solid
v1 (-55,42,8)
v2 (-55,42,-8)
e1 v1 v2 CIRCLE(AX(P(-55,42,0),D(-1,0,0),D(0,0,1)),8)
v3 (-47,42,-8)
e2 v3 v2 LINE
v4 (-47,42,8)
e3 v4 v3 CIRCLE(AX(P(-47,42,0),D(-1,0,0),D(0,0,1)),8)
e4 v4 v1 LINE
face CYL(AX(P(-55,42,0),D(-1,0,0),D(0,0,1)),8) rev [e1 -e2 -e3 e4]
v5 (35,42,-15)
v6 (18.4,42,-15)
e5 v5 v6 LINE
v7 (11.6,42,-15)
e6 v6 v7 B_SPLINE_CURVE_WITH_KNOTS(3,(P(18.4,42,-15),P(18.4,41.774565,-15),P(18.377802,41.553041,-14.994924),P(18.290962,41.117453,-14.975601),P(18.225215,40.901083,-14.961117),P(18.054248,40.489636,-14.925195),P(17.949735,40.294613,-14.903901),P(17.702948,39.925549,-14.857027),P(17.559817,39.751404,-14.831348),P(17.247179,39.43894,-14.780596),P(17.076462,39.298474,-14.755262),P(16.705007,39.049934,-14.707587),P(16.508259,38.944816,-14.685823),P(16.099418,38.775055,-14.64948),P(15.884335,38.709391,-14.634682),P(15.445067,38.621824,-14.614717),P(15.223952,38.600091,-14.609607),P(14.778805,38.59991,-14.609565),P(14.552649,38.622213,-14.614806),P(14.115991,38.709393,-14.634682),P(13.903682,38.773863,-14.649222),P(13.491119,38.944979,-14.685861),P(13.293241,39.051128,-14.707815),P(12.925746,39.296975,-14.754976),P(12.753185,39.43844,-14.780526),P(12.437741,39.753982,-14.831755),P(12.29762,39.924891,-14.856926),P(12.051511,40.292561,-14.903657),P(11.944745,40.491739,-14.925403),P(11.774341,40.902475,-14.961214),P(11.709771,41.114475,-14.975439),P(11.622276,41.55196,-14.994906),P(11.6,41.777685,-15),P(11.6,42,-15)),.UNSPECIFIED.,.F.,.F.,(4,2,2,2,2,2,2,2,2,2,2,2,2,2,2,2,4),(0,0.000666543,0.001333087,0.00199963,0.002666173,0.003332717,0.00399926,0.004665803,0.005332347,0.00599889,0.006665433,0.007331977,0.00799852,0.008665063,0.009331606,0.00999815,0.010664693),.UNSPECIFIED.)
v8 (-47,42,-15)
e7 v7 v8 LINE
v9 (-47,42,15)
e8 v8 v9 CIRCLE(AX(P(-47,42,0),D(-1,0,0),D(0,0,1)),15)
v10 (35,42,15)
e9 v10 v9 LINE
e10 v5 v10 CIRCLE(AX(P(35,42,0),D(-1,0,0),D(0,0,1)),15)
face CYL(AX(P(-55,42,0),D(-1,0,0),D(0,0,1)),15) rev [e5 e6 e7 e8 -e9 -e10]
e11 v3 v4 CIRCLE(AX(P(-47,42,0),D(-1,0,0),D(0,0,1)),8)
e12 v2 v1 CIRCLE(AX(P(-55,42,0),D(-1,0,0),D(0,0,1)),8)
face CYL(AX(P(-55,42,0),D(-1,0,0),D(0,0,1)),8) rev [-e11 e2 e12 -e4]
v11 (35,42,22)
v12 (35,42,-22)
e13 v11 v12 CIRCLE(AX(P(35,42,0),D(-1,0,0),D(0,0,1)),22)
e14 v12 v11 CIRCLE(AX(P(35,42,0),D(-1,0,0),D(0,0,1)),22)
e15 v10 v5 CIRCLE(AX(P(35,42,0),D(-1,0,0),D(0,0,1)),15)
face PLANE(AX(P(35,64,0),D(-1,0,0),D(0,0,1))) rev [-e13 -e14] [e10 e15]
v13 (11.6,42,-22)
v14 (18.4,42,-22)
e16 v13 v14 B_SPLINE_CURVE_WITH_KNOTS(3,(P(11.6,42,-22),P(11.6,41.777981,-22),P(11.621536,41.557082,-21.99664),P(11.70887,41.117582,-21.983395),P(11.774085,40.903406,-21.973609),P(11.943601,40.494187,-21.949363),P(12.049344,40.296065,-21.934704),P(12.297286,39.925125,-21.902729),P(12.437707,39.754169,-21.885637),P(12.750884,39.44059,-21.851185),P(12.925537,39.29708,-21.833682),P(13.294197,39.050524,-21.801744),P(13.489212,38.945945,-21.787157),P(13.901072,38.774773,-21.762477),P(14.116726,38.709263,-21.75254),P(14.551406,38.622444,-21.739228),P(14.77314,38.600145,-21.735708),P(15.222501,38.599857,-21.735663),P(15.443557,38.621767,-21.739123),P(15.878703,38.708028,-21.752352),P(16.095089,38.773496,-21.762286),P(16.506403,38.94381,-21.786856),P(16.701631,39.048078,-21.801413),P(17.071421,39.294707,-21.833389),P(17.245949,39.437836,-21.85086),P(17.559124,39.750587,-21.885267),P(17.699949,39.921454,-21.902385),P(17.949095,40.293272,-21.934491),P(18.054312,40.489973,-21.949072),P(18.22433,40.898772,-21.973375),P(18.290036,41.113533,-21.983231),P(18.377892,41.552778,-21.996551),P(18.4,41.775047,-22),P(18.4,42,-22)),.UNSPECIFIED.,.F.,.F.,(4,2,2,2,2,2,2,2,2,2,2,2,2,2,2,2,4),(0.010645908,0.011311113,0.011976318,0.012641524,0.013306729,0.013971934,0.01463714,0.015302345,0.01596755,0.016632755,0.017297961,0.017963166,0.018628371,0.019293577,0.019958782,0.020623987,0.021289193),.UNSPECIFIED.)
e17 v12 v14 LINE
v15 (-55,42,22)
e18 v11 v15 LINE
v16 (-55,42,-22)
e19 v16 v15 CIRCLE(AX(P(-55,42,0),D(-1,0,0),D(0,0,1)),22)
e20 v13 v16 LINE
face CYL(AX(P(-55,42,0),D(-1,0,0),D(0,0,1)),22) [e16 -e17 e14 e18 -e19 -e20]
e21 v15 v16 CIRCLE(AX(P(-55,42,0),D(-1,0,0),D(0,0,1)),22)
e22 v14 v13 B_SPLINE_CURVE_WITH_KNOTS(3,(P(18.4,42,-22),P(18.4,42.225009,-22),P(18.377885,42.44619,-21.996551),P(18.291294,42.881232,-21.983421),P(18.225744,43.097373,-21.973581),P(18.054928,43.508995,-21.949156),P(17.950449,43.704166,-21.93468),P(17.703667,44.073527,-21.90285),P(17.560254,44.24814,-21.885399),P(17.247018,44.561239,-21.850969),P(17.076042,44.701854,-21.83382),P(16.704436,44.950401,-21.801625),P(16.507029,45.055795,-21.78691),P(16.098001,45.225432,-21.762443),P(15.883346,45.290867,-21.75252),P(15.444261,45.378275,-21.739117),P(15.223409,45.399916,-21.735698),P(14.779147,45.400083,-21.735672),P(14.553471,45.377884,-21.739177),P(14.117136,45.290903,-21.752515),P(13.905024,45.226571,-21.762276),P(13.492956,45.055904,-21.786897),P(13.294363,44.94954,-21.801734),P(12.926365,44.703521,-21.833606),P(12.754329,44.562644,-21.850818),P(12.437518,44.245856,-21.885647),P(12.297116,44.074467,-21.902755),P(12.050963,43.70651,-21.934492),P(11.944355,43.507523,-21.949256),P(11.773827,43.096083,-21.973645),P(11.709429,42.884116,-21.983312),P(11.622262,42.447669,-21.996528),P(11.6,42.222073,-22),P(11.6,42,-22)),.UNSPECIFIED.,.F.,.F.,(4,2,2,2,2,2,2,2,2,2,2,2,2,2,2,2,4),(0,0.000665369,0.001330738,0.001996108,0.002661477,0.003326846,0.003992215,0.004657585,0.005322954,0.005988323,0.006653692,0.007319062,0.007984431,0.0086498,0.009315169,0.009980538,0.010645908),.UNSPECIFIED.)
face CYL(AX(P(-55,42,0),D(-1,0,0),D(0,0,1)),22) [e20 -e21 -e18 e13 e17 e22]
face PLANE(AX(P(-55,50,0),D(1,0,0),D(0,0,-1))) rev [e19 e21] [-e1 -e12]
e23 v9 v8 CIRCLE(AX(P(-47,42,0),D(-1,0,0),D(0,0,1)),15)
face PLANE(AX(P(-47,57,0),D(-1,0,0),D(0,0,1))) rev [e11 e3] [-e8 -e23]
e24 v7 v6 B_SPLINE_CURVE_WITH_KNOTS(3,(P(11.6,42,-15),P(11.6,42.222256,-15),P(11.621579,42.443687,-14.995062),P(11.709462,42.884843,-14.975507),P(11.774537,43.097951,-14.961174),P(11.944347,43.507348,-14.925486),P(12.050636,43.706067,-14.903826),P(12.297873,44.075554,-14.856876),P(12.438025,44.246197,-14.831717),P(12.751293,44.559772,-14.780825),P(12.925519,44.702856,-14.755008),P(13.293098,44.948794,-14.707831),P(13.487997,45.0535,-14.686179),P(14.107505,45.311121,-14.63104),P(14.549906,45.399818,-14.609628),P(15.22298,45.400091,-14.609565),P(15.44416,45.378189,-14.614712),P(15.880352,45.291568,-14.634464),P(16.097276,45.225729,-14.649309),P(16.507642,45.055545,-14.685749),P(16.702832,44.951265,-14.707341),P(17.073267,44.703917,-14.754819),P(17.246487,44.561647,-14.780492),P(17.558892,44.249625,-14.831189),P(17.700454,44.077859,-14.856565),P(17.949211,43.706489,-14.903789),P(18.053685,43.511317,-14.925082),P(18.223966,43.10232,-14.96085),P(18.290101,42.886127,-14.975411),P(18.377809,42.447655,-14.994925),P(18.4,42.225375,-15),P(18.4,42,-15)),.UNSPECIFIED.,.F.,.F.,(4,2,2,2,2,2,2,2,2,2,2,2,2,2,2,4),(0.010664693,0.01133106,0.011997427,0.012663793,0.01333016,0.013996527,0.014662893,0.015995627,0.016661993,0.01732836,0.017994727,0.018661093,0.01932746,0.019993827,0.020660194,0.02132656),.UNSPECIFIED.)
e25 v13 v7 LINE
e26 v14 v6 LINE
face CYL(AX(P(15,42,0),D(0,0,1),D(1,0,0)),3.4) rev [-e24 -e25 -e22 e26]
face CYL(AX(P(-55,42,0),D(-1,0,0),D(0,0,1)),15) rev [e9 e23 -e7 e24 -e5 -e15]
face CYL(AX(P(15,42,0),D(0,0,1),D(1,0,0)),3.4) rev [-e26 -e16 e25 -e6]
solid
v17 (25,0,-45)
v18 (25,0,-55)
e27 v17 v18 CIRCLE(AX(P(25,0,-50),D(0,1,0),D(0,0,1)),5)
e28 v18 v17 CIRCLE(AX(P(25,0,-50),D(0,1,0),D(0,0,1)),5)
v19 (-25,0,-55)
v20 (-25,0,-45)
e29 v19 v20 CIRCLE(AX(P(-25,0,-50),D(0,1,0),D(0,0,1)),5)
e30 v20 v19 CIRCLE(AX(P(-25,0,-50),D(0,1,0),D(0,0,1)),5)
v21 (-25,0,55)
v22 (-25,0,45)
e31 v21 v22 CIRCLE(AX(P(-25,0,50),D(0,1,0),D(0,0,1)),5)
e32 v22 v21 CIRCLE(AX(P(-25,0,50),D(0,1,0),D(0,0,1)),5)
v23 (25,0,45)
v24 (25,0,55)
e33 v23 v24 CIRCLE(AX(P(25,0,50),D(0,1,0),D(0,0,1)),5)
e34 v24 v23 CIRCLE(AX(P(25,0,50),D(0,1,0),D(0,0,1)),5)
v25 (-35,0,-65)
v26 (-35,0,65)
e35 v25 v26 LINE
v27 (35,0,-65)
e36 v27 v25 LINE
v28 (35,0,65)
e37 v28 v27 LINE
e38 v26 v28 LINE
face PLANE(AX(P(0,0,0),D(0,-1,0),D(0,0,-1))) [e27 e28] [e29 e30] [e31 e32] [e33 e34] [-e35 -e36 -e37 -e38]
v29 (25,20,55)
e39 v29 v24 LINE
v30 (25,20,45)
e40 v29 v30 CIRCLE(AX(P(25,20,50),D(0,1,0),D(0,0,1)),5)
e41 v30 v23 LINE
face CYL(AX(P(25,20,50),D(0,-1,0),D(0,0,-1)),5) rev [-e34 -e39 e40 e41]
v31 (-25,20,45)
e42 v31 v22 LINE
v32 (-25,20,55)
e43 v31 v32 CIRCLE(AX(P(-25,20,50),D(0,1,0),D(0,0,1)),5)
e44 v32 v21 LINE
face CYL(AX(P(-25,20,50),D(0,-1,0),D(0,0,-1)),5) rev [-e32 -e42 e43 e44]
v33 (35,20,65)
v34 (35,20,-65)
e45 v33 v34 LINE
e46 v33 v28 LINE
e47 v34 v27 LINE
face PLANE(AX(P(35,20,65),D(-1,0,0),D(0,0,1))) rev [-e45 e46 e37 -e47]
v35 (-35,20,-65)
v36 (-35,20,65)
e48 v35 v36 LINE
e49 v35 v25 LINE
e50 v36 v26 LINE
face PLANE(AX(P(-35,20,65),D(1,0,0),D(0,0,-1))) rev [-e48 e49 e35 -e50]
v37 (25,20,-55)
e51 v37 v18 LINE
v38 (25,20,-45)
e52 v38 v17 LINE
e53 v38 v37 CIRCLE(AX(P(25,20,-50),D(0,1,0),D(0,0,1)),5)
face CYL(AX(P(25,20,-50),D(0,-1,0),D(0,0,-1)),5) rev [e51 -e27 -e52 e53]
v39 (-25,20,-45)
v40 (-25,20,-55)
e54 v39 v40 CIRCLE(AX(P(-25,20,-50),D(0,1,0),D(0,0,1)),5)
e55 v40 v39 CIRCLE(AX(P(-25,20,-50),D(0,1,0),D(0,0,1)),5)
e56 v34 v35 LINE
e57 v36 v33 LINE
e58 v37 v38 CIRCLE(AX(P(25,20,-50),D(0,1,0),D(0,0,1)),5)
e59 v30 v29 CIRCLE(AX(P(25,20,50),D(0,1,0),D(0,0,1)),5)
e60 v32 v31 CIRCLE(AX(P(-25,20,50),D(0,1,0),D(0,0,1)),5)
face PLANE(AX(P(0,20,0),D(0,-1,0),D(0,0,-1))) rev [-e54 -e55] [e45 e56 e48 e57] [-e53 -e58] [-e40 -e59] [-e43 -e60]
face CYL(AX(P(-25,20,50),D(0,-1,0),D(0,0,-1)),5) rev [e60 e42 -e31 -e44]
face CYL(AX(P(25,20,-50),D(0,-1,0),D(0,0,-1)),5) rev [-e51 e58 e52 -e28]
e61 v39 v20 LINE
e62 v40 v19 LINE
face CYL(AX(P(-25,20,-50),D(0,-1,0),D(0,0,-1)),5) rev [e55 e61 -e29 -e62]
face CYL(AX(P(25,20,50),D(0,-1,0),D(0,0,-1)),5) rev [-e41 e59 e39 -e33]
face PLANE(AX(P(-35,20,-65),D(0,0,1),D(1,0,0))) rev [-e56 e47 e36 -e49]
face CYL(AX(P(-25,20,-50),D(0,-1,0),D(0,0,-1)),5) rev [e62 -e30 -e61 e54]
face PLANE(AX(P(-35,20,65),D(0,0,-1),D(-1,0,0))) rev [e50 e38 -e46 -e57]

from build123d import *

# Parameters (mm, degrees)
SKETCH_1_W      = 70
SKETCH_1_H      = 130
SKETCH_1_R      = 5
EXTRUDE_1_DEPTH = 20
SKETCH_4_W      = 3.4
SKETCH_4_H      = 65


with BuildPart() as part:
    # 草图1 → 凸台-拉伸1 (new body)
    with BuildSketch(Plane(origin=(0, 0, 0), x_dir=(1, 0, 0), z_dir=(0, 1, 0))):
        Rectangle(SKETCH_1_W, SKETCH_1_H)
        with Locations(Location((-25, -50, 0), (0, 0, 270))):
            Circle(SKETCH_1_R, mode=Mode.SUBTRACT)
        with Locations(Location((25, -50, 0), (0, 0, 270))):
            Circle(SKETCH_1_R, mode=Mode.SUBTRACT)
        with Locations(Location((25, 50, 0), (0, 0, 270))):
            Circle(SKETCH_1_R, mode=Mode.SUBTRACT)
        with Locations(Location((-25, 50, 0), (0, 0, 270))):
            Circle(SKETCH_1_R, mode=Mode.SUBTRACT)
    extrude(amount=EXTRUDE_1_DEPTH)


with BuildPart() as body_2:
    # 草图2 → 旋转1 (revolve)
    with BuildSketch(Plane.XY, mode=Mode.PRIVATE) as revolve_1_sk:
        Polygon((-55, 50), (-47, 50), (-47, 57), (35, 57), (35, 64), (-55, 64), align=None)
    revolve(revolve_1_sk.sketch.rotate(Axis((-55, 42, 0), (1, 0, 0)), 90), axis=Axis((-55, 42, 0), (1, 0, 0)))

    # 草图4 → M8 螺纹孔1 (revolve, cut)
    with BuildSketch(Plane(origin=(15, 42, 0), x_dir=(0, -1, 0), z_dir=(1, 0, 0))):
        with Locations((1.7, 32.5)):
            Rectangle(SKETCH_4_W, SKETCH_4_H)
    revolve(axis=Axis((15, 42, 6.35), (0, 0, -1)), mode=Mode.SUBTRACT)


solid = Compound([part.part, body_2.part])
